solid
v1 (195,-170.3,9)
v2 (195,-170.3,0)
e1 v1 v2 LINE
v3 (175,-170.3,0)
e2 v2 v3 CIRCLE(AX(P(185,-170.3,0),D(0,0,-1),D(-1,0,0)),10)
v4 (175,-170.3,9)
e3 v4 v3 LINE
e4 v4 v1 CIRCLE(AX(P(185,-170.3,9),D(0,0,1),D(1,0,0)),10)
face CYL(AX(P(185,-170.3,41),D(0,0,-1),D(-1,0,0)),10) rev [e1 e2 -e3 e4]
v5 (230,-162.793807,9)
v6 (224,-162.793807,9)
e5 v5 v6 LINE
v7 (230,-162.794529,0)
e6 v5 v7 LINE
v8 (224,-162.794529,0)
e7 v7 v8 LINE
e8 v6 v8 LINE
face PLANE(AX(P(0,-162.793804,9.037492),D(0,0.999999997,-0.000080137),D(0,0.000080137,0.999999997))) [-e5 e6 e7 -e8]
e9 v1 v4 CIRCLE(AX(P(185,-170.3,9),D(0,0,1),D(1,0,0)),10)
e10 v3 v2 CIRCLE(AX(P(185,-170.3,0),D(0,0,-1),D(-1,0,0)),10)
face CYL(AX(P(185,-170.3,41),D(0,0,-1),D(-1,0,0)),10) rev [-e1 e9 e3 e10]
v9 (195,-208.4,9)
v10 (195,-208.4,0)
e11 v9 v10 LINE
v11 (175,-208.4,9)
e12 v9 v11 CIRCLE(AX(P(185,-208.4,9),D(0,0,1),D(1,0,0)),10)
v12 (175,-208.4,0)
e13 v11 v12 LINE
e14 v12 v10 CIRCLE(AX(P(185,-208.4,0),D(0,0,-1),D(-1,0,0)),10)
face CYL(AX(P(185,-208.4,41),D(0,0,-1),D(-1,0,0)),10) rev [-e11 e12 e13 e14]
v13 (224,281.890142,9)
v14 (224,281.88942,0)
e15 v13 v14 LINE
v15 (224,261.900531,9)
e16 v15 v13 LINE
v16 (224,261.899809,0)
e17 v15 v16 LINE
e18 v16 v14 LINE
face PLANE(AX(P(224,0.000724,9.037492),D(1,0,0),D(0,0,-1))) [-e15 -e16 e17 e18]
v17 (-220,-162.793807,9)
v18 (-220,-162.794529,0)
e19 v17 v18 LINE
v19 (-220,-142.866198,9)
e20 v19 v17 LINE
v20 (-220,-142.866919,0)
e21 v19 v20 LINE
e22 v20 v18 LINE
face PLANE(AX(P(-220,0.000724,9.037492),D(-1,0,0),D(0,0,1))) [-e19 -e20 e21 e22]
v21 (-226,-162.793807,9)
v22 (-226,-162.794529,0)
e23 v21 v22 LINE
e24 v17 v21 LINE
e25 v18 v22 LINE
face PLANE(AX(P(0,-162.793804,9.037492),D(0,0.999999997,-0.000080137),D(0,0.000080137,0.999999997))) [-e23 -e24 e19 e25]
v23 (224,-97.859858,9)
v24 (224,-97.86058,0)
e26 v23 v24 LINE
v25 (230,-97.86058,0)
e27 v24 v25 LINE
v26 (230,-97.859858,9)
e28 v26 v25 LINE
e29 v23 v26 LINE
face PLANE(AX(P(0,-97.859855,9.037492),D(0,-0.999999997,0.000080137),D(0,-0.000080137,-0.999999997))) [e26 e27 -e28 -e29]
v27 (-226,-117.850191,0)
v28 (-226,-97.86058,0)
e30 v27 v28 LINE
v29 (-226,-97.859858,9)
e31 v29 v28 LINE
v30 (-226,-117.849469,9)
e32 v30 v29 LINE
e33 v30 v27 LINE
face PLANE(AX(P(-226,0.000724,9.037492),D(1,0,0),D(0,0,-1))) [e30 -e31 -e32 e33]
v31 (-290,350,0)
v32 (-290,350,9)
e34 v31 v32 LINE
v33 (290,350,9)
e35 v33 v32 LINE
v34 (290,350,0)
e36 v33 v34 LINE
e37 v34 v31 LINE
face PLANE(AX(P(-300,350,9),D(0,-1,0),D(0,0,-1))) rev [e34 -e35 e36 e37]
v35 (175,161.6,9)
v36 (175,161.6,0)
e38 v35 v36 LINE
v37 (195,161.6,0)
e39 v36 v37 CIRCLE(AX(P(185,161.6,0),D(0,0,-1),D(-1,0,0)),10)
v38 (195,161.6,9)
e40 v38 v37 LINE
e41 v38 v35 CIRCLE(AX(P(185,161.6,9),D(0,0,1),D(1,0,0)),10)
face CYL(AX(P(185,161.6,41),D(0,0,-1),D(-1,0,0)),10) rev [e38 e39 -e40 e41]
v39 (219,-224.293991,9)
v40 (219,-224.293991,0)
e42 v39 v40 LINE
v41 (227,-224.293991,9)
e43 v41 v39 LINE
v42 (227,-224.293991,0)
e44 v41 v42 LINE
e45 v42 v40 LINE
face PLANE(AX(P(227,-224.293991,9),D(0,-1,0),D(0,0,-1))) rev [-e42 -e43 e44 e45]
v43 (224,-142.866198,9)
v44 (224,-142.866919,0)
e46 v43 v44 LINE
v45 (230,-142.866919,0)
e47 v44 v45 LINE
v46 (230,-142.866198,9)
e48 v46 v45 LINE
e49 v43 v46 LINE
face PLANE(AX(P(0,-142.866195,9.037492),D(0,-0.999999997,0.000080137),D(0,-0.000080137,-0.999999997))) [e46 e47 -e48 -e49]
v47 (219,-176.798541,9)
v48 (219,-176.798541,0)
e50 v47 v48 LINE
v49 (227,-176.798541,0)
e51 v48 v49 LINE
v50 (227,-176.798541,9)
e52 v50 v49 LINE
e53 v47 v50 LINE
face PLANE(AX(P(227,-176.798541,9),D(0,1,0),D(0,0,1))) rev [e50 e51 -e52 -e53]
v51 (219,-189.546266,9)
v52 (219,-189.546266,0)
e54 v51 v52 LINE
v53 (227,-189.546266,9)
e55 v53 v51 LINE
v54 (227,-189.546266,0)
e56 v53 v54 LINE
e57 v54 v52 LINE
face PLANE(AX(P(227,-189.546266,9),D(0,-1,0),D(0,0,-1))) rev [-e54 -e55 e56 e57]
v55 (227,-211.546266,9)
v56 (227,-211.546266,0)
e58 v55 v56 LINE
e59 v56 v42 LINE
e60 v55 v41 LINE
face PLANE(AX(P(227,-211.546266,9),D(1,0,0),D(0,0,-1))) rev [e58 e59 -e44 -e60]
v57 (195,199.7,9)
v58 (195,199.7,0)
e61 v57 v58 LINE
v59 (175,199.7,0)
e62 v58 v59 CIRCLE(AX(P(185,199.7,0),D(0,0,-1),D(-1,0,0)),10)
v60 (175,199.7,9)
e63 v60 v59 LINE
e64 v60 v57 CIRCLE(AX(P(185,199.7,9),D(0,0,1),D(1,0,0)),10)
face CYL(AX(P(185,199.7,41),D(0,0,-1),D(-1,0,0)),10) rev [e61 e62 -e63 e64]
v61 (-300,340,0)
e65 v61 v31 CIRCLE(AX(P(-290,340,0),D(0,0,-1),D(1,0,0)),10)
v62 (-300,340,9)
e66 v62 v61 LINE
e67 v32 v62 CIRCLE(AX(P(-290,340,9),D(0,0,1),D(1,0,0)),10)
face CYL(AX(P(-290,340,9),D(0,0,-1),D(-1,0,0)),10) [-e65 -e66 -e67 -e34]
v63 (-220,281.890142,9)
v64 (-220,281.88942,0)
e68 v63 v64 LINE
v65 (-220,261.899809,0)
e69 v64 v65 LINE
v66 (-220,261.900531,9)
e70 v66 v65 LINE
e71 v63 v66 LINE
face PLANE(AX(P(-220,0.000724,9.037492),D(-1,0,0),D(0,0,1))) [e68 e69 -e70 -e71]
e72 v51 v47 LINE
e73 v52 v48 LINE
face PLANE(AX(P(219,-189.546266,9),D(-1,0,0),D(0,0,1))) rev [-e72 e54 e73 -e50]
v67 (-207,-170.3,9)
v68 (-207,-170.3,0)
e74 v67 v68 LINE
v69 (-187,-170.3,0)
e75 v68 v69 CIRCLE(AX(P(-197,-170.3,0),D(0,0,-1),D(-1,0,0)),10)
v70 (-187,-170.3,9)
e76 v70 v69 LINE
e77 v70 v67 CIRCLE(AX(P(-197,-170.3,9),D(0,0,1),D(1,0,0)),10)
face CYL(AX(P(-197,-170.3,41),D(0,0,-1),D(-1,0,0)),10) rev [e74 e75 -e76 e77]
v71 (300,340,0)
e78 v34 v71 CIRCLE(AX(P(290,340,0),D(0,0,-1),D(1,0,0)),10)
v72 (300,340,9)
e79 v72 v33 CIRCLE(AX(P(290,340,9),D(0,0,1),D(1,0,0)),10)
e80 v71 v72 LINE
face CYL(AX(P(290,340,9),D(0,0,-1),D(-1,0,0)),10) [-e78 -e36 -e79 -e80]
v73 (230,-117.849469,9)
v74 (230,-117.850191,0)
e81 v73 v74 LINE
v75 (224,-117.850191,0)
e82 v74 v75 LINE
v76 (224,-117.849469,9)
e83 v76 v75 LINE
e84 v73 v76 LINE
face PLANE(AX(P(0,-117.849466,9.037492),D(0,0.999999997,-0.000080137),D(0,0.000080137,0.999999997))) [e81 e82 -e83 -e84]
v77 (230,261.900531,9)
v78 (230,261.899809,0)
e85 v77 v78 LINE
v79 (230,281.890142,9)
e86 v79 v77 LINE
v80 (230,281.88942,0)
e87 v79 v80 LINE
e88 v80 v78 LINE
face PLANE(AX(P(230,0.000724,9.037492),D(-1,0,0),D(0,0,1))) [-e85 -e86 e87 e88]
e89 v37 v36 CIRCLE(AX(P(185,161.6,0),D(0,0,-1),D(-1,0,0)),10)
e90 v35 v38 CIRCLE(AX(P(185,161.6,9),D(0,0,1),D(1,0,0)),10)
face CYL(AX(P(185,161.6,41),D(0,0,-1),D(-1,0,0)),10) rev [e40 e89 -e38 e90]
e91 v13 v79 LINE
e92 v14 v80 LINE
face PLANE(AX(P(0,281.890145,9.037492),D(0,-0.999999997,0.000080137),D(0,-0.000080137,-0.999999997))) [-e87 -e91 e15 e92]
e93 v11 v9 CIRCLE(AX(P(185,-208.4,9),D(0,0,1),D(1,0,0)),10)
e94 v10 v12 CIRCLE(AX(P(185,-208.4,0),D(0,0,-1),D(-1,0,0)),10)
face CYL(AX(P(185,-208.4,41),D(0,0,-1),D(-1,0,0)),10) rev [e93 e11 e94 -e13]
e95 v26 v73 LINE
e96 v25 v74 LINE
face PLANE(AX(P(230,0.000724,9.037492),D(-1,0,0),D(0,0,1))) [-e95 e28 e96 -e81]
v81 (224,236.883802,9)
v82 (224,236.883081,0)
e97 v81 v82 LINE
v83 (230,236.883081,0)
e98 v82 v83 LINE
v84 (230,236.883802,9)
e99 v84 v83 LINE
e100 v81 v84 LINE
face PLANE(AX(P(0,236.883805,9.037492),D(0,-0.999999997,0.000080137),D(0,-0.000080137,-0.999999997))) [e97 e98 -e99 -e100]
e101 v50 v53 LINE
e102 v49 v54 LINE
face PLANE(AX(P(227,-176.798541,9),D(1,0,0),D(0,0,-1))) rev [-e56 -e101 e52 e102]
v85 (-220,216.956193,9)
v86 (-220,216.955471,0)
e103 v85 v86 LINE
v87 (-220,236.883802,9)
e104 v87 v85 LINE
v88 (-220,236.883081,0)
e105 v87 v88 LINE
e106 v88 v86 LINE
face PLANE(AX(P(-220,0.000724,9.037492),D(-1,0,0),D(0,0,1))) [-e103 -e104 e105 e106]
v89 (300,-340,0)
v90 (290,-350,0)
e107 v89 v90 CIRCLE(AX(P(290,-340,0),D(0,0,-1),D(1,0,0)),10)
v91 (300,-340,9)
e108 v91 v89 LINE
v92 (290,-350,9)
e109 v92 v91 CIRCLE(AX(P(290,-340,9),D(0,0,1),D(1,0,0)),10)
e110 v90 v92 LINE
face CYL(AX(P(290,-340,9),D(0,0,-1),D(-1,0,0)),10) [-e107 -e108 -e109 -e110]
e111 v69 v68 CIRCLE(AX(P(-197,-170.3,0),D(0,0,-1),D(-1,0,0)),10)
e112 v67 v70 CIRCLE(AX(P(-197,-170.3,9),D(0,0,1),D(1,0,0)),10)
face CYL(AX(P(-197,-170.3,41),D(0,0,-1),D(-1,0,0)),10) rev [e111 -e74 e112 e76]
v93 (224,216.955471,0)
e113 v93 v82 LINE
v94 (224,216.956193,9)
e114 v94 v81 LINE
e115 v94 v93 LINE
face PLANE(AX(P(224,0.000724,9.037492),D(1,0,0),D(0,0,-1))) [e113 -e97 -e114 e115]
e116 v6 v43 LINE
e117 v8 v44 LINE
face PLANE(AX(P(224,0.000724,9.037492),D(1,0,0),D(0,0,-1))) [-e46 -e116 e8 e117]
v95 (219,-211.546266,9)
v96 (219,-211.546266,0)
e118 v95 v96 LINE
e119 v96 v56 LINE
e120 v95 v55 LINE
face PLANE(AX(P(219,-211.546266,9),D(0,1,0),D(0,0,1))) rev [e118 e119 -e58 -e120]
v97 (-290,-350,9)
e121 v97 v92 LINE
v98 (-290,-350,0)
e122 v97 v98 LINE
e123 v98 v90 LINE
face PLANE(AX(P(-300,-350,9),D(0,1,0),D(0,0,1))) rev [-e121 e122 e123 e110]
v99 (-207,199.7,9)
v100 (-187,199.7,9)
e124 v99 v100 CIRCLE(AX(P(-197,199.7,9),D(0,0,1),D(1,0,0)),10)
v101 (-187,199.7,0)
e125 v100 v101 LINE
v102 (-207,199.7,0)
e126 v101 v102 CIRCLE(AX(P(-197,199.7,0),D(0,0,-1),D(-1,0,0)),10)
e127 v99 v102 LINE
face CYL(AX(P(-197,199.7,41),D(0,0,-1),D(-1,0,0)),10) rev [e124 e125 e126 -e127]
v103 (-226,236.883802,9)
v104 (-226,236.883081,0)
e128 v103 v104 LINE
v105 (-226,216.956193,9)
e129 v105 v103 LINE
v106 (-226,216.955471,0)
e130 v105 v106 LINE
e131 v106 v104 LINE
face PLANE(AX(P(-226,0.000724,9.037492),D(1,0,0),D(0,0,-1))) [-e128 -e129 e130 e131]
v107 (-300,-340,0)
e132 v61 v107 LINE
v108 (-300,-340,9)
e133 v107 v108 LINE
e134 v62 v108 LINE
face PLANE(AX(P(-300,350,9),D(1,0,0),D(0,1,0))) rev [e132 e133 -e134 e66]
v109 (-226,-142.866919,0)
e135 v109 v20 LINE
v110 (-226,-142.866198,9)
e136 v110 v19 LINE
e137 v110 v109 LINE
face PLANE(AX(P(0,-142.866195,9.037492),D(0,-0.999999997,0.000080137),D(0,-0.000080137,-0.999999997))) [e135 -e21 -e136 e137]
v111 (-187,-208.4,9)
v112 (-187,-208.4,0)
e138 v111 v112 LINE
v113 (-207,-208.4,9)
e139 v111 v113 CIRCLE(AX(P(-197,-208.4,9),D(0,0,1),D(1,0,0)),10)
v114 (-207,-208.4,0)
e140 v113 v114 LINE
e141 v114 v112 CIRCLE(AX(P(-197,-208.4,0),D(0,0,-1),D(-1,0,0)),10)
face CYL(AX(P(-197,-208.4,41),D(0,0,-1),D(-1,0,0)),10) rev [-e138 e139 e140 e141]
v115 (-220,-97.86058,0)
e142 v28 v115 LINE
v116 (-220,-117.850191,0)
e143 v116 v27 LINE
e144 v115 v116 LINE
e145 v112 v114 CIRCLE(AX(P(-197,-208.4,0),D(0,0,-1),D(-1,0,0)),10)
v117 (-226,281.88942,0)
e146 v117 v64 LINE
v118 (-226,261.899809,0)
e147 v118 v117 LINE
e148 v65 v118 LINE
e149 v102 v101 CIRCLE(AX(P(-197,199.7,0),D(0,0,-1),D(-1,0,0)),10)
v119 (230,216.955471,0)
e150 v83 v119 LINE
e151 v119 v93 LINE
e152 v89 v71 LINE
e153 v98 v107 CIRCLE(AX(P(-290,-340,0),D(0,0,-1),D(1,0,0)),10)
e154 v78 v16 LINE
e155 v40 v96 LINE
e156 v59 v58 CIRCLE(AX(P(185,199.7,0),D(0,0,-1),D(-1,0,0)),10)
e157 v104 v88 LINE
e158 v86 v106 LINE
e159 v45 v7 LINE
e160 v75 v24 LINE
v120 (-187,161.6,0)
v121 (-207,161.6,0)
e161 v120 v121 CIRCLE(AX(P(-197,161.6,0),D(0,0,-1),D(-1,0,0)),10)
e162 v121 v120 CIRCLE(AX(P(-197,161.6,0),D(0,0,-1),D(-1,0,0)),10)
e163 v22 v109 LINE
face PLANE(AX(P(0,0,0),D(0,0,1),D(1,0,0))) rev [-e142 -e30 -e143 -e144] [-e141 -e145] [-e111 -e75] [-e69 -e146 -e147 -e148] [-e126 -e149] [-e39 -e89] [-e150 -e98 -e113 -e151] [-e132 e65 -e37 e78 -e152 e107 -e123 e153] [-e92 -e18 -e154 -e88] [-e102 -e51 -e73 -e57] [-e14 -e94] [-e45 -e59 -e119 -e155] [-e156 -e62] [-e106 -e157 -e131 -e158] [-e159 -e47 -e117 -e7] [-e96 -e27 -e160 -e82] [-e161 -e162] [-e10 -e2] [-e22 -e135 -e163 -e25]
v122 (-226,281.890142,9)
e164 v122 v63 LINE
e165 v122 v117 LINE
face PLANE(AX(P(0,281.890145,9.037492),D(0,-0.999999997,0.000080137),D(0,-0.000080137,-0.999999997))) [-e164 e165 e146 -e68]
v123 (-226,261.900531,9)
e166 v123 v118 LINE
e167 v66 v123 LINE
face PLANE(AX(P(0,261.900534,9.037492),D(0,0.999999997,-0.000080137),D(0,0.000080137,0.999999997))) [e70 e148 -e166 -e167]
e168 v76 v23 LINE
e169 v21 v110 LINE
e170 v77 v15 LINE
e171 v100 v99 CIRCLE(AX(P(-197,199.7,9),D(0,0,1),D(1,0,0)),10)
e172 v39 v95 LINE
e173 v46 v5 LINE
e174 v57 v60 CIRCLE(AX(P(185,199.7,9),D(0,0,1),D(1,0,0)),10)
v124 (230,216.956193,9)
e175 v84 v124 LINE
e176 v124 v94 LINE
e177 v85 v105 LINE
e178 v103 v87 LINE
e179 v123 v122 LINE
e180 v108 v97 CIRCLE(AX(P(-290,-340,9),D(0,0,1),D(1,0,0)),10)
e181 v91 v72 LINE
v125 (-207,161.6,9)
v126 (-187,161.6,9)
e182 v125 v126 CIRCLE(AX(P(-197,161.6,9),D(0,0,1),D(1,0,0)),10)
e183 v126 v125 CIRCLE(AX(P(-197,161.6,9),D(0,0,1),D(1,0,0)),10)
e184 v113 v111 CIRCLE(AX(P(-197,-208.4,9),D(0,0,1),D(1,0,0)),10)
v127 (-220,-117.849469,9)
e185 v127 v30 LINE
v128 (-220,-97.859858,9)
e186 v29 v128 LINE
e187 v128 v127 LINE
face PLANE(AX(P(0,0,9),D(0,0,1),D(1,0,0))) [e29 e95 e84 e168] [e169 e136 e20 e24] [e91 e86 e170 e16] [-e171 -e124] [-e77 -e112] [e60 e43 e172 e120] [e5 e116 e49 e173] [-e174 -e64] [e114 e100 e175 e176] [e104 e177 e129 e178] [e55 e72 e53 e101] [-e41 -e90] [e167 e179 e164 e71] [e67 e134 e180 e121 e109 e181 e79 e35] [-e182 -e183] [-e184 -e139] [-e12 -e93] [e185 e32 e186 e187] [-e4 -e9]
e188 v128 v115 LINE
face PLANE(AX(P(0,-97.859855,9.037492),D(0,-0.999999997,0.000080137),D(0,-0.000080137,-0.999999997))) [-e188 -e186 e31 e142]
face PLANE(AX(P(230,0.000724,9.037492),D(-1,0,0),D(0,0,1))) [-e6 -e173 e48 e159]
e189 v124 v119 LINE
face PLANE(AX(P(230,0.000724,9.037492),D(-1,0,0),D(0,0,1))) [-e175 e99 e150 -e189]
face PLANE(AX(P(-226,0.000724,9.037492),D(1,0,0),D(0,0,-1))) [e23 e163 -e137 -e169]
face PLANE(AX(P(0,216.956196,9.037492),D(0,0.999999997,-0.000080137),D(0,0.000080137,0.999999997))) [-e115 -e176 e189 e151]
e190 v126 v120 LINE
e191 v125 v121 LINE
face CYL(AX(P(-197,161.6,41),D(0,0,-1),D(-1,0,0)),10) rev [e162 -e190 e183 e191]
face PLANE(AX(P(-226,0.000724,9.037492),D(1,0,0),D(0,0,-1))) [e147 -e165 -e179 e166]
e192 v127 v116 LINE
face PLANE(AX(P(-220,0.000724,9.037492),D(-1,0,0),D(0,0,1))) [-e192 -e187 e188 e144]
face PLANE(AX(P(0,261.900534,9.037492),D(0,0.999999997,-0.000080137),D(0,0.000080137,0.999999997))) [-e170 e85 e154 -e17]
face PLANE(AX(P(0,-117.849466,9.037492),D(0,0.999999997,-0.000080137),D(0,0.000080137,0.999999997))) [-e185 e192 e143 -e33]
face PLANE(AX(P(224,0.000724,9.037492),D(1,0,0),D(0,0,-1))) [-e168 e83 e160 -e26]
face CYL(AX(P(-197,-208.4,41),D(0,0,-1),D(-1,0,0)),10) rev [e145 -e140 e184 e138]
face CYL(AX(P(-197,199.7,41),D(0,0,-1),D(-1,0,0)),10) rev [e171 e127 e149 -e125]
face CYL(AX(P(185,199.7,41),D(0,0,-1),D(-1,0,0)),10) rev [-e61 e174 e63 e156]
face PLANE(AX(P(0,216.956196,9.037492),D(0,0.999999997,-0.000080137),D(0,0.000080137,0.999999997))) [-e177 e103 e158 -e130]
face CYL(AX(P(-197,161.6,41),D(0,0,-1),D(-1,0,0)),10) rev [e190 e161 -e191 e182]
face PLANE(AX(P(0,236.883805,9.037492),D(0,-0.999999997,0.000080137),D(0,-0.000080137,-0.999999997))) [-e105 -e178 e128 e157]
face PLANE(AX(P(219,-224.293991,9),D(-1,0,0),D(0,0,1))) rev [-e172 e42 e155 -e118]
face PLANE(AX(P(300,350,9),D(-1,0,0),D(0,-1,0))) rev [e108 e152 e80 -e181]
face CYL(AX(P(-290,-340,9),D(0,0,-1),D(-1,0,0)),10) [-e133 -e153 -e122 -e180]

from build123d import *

# Parameters (mm, degrees)
SKETCH1_W                   = 600
SKETCH1_H                   = 700
BOSS_EXTRUDE1_DEPTH         = 9
FILLET1_R                   = 10
SKETCH3_R                   = 10
CUT_EXTRUDE2_DEPTH          = 41
SKETCH7_W                   = 8
SKETCH7_H                   = 12.747725193
CUT_EXTRUDE4_DEPTH          = 483.221865906
CUT_EXTRUDE8_START          = -499.177752008
SKETCH11_W                  = 6
SKETCH11_H                  = 19.989610894
SKETCH11_H_2                = 19.927609768
CUT_EXTRUDE8_DEPTH          = 881.951690015
LPATTERN4_COUNT             = 2
LPATTERN4_PITCH             = 379.75
LPATTERN5_COUNT             = 2
LPATTERN5_PITCH             = 450
LPATTERN5_START             = -499.177752008
LPATTERN5_COPY_1_SKETCH_W   = 6
LPATTERN5_COPY_1_SKETCH_H   = 19.989610894
LPATTERN5_COPY_1_SKETCH_H_2 = 19.927609768
LPATTERN5_COPY_1_DEPTH      = 881.951690015


with BuildPart() as part:
    # Sketch1 → Boss-Extrude1 (new body)
    with BuildSketch(Plane.XY):
        Rectangle(SKETCH1_W, SKETCH1_H)
    extrude(amount=BOSS_EXTRUDE1_DEPTH)

    # Fillet1
    fillet1_edges = [part.edges().sort_by_distance(p)[0] for p in [
        (300, -350, 4.5),
        (-300, -350, 4.5),
        (-300, 350, 4.5),
        (300, 350, 4.5),
    ]]
    fillet(fillet1_edges, radius=FILLET1_R)

    # Sketch3 → Cut-Extrude2 (cut)
    with BuildSketch(Plane(origin=(-23.01798078, 7.933390522, 0), x_dir=(-1, 0, 0), z_dir=(0, 0, -1))):
        with Locations((-208.01798078, 153.666609478)):
            Circle(SKETCH3_R)
        with Locations((-208.01798078, -216.333390522)):
            Circle(SKETCH3_R)
        with Locations((-208.01798078, -178.233390522)):
            Circle(SKETCH3_R)
        with Locations((173.98201922, 191.766609478)):
            Circle(SKETCH3_R)
        with Locations((173.98201922, 153.666609478)):
            Circle(SKETCH3_R)
        with Locations((173.98201922, -178.233390522)):
            Circle(SKETCH3_R)
        with Locations((173.98201922, -216.333390522)):
            Circle(SKETCH3_R)
        with Locations((-208.01798078, 191.766609478)):
            Circle(SKETCH3_R)
    extrude(amount=-CUT_EXTRUDE2_DEPTH, mode=Mode.SUBTRACT)

    # Sketch7 → Cut-Extrude4 (cut, through all)
    with BuildSketch(Plane(origin=(-23.01798078, 7.933390522, 0), x_dir=(-1, 0, 0), z_dir=(0, 0, -1))):
        with Locations((-246.01798078, -191.1057938)):
            Rectangle(SKETCH7_W, SKETCH7_H)
        with Locations((-246.01798078, -225.853518993)):
            Rectangle(SKETCH7_W, SKETCH7_H)
    extrude(amount=-CUT_EXTRUDE4_DEPTH, mode=Mode.SUBTRACT)

    # Sketch11 → Cut-Extrude8 (cut)
    with BuildSketch(Plane(origin=(-23.01798078, 7.93041319, -116.40444969), x_dir=(-1, 0, 0), z_dir=(1.1016286228319074e-14, -8.013698647454937e-05, -0.9999999967890317)).offset(CUT_EXTRUDE8_START)):
        with Locations((199.98201922, -115.795126315)):
            Rectangle(SKETCH11_W, SKETCH11_H)
        with Locations((199.98201922, -160.770464654)):
            Rectangle(SKETCH11_W, SKETCH11_H_2)
    cut_extrude8 = extrude(amount=CUT_EXTRUDE8_DEPTH, mode=Mode.SUBTRACT)

    # LPattern4: Cut-Extrude8 ×2
    with Locations(*[Vector(0, 0.9999999967890317, -8.013698647454937e-05) * (i * LPATTERN4_PITCH) for i in range(1, LPATTERN4_COUNT)]):
        add(cut_extrude8, mode=Mode.SUBTRACT)

    # LPattern5: Cut-Extrude8 ×2
    with Locations(*[(i * LPATTERN5_PITCH, 0, 0) for i in range(1, LPATTERN5_COUNT)]):
        add(cut_extrude8, mode=Mode.SUBTRACT)

    # LPattern5 copy 1 sketch → LPattern5 copy 1 (cut)
    with BuildSketch(Plane(origin=(426.98201922, 387.680411971, -116.434881711), x_dir=(-1, 0, 0), z_dir=(1.1016286228319074e-14, -8.013698647454937e-05, -0.9999999967890317)).offset(LPATTERN5_START)):
        with Locations((199.98201922, -115.795126315)):
            Rectangle(LPATTERN5_COPY_1_SKETCH_W, LPATTERN5_COPY_1_SKETCH_H)
        with Locations((199.98201922, -160.770464654)):
            Rectangle(LPATTERN5_COPY_1_SKETCH_W, LPATTERN5_COPY_1_SKETCH_H_2)
    extrude(amount=LPATTERN5_COPY_1_DEPTH, mode=Mode.SUBTRACT)


solid = part.part
